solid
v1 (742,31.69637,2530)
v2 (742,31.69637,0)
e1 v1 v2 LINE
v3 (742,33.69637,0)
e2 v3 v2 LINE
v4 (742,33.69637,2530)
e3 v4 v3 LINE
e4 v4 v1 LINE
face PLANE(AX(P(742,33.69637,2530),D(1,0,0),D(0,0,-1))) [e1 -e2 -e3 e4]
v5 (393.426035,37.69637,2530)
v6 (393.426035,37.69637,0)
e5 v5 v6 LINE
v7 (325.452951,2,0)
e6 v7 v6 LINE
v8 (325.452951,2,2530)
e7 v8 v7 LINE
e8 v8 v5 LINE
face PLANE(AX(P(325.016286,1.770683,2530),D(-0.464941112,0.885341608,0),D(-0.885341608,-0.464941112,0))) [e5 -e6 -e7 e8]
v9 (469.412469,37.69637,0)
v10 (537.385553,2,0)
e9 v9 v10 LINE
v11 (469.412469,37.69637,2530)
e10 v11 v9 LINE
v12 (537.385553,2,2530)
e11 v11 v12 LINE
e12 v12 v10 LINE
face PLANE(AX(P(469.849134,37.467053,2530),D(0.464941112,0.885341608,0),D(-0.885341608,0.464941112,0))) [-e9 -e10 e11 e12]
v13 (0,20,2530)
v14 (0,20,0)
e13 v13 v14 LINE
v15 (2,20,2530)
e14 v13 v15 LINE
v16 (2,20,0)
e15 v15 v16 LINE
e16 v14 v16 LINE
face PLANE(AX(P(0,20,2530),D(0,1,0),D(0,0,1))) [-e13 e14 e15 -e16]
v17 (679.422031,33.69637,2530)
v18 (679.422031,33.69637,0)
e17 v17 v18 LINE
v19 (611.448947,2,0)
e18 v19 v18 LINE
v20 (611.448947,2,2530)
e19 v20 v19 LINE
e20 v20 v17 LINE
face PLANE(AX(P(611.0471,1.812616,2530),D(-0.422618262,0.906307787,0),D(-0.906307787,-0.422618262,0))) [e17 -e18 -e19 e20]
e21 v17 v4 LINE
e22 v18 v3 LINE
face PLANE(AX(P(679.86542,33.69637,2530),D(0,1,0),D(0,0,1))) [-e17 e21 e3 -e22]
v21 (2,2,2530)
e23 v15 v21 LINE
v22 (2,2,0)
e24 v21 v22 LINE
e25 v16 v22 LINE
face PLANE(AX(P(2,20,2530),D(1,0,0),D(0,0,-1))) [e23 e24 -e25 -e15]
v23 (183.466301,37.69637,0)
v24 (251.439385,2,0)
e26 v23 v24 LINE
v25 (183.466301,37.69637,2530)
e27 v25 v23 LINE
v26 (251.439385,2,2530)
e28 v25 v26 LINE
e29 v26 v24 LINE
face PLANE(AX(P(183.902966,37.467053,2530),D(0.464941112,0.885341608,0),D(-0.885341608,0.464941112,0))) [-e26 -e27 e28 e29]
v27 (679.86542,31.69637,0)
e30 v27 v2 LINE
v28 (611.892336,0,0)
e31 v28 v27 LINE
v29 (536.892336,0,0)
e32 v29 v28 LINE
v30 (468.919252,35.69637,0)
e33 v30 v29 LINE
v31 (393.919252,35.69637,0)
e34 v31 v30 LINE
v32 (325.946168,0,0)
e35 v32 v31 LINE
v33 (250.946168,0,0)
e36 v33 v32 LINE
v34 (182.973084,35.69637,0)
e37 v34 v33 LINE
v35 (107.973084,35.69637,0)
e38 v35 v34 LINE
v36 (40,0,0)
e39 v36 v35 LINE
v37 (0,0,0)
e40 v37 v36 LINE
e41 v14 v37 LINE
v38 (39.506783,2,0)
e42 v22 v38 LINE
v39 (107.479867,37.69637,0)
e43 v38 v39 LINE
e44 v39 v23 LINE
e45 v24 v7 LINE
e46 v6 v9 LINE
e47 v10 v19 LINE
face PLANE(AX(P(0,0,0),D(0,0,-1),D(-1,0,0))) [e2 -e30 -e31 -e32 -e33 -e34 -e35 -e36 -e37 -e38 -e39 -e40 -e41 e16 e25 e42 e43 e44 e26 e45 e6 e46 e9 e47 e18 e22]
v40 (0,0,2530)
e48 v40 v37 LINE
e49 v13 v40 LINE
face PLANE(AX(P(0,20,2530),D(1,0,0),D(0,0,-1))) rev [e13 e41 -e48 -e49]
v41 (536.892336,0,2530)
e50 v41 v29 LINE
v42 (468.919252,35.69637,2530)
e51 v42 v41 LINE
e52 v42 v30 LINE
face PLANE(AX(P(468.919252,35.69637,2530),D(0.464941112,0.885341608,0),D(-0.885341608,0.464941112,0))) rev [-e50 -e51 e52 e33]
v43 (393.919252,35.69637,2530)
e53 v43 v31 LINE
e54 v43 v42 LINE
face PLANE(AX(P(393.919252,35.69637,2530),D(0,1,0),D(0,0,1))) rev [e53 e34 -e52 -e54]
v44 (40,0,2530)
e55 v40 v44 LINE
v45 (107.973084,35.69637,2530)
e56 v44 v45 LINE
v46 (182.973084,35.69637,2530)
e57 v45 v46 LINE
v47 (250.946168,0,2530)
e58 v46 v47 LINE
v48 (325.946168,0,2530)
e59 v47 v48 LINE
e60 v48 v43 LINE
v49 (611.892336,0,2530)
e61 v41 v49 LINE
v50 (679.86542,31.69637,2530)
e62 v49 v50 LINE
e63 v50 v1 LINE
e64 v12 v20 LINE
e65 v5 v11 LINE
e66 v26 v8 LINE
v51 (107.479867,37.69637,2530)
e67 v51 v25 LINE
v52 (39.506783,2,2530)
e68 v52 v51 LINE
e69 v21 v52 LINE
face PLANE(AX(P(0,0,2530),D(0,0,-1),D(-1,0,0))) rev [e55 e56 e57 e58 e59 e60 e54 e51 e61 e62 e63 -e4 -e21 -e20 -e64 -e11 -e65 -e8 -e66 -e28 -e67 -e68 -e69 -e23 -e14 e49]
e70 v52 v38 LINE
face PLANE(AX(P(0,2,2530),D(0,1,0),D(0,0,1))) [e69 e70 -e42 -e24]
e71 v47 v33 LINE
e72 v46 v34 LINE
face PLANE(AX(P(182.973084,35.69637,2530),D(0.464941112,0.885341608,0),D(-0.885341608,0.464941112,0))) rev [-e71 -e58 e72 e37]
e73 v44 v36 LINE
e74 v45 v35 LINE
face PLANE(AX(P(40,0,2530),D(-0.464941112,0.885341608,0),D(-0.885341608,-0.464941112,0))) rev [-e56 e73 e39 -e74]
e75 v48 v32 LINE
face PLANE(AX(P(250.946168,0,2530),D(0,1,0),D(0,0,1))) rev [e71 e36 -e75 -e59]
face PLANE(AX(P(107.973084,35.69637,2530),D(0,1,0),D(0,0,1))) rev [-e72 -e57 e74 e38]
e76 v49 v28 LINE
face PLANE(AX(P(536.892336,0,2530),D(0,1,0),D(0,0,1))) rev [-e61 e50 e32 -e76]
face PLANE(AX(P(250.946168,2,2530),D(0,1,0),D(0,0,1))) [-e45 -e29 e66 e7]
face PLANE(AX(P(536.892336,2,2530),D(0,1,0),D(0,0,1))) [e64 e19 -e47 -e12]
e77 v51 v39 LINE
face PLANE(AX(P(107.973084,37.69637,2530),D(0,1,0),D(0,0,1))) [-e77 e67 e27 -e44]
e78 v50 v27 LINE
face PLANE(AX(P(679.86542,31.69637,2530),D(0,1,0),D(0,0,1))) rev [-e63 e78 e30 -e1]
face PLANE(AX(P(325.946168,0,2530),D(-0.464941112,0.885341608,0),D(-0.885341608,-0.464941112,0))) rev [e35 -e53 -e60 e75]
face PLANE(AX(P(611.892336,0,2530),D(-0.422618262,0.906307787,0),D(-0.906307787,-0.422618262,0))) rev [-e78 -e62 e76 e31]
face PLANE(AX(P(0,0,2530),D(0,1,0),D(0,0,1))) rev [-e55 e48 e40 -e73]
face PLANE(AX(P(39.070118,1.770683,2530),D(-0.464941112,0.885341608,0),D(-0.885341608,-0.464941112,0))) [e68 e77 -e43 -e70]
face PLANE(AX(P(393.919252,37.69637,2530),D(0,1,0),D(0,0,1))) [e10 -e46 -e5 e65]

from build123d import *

# Parameters (mm, degrees)
EXTRUDE_THIN1_DEPTH = 2530


with BuildPart() as part:
    # Sketch1 → Extrude-Thin1 (new body)
    with BuildSketch(Plane.XY):
        Polygon((0, 20), (0, 0), (40, 0), (107.973084028, 35.696369631), (182.973084028, 35.696369631), (250.946168056, 0), (325.946168056, 0), (393.919252083, 35.696369631), (468.919252083, 35.696369631), (536.892336111, 0), (611.892336111, 0), (679.865420139, 31.696369631), (742.000000002, 31.696369631), (742.000000002, 33.696369631), (679.422030814, 33.696369631), (611.448946786, 2), (537.385552948, 2), (469.41246892, 37.696369631), (393.426035246, 37.696369631), (325.452951219, 2), (251.439384892, 2), (183.466300865, 37.696369631), (107.479867191, 37.696369631), (39.506783163, 2), (2, 2), (2, 20), align=None)
    extrude(amount=EXTRUDE_THIN1_DEPTH)


solid = part.part
